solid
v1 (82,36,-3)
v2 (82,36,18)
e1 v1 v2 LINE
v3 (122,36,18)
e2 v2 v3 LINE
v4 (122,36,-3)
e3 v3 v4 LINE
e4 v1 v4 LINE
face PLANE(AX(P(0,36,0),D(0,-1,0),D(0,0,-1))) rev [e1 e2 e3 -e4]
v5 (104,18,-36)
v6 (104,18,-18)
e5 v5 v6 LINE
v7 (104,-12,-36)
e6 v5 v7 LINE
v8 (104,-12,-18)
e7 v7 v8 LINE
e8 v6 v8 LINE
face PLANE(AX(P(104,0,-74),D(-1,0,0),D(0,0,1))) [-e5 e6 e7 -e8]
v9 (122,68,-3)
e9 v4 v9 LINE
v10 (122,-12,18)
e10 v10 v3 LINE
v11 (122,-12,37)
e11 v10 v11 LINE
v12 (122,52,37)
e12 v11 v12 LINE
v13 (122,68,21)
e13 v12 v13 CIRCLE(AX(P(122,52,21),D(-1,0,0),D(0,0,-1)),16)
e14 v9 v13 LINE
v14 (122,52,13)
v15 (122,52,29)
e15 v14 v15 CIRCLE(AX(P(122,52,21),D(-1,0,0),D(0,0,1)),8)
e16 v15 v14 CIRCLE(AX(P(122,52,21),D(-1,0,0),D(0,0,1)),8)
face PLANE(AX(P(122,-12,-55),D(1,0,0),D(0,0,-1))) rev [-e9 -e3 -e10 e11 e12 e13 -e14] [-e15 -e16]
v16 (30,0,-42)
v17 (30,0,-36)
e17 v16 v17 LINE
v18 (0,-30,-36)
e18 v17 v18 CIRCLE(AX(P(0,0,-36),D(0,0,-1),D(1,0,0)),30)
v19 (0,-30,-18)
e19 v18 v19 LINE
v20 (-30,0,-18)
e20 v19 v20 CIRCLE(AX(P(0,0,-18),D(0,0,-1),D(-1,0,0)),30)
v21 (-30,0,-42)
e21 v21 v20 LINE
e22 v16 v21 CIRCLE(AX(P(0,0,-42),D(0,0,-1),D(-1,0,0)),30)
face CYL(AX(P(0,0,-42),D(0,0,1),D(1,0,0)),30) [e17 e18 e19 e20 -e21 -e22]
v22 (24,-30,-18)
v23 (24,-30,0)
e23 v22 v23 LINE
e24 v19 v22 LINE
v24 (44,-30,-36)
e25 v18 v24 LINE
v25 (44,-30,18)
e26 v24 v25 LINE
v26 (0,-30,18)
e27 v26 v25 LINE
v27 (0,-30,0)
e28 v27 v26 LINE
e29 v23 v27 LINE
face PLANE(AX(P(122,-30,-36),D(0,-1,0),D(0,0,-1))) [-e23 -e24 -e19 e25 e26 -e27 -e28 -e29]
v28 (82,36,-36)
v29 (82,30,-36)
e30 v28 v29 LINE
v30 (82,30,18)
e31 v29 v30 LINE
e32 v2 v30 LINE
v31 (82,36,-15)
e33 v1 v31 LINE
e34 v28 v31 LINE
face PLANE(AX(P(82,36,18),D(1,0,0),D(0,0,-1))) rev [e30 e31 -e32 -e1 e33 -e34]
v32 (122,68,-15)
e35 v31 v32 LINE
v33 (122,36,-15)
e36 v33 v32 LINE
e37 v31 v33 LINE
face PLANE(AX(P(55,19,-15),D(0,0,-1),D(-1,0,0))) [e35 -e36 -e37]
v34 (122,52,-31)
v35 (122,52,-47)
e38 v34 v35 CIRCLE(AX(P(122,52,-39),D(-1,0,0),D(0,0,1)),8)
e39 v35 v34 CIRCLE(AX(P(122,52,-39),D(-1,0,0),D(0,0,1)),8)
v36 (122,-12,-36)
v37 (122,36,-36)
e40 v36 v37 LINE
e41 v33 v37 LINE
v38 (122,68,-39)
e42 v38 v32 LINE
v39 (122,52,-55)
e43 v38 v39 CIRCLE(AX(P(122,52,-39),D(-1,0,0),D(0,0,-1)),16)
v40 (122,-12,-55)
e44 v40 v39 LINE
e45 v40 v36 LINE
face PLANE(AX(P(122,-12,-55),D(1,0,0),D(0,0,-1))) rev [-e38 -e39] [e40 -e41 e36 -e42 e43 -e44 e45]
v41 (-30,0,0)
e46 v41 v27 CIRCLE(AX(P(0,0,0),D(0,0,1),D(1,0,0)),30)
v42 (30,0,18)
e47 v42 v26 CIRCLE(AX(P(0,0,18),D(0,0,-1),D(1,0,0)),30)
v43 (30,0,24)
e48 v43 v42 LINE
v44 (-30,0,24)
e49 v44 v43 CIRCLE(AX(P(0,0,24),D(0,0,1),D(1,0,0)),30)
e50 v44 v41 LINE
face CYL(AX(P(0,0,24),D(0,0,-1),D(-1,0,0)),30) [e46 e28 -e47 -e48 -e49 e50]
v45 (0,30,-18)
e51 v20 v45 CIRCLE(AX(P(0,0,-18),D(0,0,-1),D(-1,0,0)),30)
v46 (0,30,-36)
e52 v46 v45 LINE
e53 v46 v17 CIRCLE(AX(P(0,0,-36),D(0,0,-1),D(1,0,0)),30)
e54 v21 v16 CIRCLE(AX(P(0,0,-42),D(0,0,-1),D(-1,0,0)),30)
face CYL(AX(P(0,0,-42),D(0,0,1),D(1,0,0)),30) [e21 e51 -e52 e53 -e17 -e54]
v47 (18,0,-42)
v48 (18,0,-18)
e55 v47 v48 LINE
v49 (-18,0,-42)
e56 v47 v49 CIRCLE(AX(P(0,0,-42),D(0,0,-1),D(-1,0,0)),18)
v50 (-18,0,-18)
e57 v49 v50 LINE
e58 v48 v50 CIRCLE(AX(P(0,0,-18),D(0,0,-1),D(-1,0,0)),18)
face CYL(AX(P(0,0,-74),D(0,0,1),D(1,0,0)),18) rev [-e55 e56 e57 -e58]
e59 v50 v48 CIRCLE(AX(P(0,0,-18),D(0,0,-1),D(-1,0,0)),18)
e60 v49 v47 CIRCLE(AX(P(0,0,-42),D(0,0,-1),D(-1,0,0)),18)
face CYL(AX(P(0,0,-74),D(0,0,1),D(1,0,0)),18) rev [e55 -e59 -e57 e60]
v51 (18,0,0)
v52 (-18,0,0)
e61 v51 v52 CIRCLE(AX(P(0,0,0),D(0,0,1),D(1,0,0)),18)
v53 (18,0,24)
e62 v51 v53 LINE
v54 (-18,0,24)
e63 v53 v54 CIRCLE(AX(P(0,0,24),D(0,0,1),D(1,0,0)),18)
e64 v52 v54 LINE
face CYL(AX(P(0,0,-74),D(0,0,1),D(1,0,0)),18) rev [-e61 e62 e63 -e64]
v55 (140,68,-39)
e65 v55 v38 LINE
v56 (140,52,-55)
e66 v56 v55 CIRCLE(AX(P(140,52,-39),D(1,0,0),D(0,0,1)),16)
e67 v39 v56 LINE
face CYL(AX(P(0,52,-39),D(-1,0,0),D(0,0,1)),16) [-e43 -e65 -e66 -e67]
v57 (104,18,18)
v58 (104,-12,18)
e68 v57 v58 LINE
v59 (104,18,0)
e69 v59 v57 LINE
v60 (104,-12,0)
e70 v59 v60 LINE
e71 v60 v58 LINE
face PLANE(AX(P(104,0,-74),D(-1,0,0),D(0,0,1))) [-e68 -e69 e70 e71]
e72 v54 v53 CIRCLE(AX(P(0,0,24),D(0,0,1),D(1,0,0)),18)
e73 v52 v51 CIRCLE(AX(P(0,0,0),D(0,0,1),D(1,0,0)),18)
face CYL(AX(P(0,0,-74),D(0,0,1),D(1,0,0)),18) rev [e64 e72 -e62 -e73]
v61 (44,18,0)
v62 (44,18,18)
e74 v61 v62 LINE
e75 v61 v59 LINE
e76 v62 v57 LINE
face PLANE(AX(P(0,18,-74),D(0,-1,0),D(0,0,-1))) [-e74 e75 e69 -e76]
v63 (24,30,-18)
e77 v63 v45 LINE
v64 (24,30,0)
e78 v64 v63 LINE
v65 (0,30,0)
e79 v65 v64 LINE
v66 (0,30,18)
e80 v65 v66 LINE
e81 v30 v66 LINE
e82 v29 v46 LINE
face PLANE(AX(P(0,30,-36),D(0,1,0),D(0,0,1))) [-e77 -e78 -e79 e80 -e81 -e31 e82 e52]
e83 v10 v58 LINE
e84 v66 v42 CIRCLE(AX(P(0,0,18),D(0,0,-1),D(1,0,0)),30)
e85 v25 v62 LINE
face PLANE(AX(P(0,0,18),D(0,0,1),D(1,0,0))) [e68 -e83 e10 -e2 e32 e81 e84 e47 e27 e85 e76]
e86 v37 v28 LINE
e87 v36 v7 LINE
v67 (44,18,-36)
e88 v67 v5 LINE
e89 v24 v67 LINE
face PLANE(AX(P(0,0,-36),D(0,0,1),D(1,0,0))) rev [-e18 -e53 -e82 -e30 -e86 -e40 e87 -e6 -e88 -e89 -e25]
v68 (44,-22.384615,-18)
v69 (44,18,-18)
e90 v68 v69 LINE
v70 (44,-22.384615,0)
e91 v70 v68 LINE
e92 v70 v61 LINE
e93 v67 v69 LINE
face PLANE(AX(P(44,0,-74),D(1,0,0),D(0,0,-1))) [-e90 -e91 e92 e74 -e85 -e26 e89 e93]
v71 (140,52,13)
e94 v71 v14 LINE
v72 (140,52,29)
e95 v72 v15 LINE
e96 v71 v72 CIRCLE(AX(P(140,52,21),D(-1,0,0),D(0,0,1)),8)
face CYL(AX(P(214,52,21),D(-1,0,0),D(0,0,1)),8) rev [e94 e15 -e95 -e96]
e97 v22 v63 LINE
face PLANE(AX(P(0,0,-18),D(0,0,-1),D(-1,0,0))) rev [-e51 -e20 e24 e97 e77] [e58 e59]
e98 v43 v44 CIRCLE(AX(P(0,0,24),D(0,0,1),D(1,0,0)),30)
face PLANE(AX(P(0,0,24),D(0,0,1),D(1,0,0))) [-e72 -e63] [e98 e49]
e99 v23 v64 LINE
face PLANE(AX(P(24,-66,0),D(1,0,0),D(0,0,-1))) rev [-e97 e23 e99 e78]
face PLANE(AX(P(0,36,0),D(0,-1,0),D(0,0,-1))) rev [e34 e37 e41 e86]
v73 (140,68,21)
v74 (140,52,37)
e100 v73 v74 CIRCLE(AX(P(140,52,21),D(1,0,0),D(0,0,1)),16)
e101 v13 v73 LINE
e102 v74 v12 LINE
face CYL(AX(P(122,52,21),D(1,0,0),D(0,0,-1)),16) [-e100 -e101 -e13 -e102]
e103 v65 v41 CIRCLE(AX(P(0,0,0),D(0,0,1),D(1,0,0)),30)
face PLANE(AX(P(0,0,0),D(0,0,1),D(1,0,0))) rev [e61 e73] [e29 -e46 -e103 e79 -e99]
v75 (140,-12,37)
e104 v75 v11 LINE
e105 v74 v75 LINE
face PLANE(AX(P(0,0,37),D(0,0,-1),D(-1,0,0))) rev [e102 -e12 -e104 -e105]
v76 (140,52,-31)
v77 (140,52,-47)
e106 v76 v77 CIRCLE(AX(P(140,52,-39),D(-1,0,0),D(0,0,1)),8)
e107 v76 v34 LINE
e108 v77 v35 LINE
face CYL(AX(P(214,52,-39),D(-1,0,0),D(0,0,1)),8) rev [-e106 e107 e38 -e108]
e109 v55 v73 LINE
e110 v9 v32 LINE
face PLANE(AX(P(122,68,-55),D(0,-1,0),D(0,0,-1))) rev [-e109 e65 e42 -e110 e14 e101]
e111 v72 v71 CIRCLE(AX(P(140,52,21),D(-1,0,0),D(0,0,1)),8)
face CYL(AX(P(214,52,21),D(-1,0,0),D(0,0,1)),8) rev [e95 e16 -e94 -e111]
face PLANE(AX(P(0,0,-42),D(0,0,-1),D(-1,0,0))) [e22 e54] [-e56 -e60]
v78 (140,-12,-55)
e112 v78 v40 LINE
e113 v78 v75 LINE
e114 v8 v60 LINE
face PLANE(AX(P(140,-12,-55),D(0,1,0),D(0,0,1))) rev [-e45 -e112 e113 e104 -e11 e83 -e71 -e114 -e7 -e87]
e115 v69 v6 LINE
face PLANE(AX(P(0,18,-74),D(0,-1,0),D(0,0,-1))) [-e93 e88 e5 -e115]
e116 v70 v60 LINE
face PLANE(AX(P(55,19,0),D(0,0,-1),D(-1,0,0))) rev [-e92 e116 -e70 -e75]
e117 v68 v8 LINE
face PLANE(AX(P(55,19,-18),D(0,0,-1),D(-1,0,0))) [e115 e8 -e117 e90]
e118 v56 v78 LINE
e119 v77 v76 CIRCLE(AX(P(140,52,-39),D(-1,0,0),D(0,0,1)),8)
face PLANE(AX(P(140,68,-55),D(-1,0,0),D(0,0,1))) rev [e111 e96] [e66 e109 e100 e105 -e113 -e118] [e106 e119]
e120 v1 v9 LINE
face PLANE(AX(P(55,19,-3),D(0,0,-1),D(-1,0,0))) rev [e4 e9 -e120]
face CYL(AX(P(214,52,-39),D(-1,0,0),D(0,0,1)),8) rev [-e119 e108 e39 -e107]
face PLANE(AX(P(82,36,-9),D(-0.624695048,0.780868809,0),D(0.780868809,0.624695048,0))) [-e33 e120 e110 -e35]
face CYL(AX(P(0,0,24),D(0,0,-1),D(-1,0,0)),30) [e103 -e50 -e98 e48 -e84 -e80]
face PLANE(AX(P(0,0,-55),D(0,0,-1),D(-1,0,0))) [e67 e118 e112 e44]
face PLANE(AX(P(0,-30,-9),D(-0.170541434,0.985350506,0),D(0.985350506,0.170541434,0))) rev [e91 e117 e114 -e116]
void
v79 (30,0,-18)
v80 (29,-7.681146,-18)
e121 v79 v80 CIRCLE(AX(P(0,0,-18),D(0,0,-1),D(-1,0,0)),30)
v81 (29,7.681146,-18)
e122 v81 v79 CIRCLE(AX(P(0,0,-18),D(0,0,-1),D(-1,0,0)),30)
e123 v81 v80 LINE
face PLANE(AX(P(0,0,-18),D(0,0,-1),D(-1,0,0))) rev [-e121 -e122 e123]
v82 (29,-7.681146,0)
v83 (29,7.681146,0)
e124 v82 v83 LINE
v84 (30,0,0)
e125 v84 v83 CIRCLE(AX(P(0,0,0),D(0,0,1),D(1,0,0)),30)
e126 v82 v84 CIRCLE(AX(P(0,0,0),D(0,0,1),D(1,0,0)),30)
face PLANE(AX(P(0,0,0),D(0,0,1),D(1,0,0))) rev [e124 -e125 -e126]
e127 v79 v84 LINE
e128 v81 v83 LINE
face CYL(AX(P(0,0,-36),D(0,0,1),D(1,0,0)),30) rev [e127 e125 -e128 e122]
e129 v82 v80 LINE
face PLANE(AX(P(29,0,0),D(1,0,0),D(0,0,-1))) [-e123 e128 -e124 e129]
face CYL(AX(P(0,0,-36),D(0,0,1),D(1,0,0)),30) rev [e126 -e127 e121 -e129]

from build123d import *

# Parameters (mm, degrees)
HUB_PROFILE_SKETCH_R         = 30
HUB_60_DEPTH                 = 24
HUB_EXTENSION_SKETCH_R       = 30
HUB_EXTENSION_60_DEPTH       = 24
HUB_BORE_SKETCH_R            = 18
HUB_BORE_36_DEPTH            = 98
ARM_START                    = -54
ARM_BODY_DEPTH               = 54
CLEVIS_SLOT_SKETCH_W         = 24
CLEVIS_SLOT_SKETCH_H         = 18
CLEVIS_SLOT_24MM_DEPTH       = 96
SLOT_PAD_SKETCH_W            = 18
SLOT_PAD_SKETCH_H            = 60
SLOT_PAD_5MM_DEPTH           = 5
RIB_BASE_PAD_SKETCH_W        = 40
RIB_BASE_PAD_SKETCH_H        = 54
RIB_BASE_PAD_DEPTH           = 6
MOUNTING_FLANGE_SKETCH_W     = 18
MOUNTING_FLANGE_SKETCH_H     = 80
MOUNTING_FLANGE_DEPTH        = 46
FLANGE_CORNER_FILLET_R16_A_R = 16
FLANGE_CORNER_FILLET_R16_B_R = 16
FLANGE_HOLES_SKETCH_R        = 8
FLANGE_HOLES_2X_16_DEPTH     = 92
FLANGE_RIB_12MM_REACH        = 164.296
FLANGE_RIB_SKETCH_WALL_W     = 377.817045558
FLANGE_RIB_SKETCH_WALL_H     = 12
ARM_RELIEF_CUT_DEPTH         = 92
ARM_RIB_18MM_REACH           = 164.296
ARM_RIB_SKETCH_WALL_W        = 432.138250074
ARM_RIB_SKETCH_WALL_H        = 18


with BuildPart() as part:
    # Hub Profile Sketch → Hub Ø60 (new body)
    with BuildSketch(Plane.XY):
        Circle(HUB_PROFILE_SKETCH_R)
    extrude(amount=HUB_60_DEPTH)


with BuildPart() as body_2:
    # Hub Extension Sketch → Hub Extension Ø60 (new body)
    with BuildSketch(Plane(origin=(0, 0, -18), x_dir=(-1, 0, 0), z_dir=(0, 0, -1))):
        with Locations(Location((0, 0, 0), (0, 0, 180))):
            Circle(HUB_EXTENSION_SKETCH_R)
    extrude(amount=HUB_EXTENSION_60_DEPTH)


with BuildPart() as hub_bore_36_tool:
    # Hub Bore Sketch → Hub Bore Ø36 (new body)
    with BuildSketch(Plane.XY.offset(24)):
        Circle(HUB_BORE_SKETCH_R)
    extrude(amount=-HUB_BORE_36_DEPTH)


with BuildPart() as part_1:
    add(part.part)

    # Hub Bore Ø36: cut by hub_bore_36_tool
    add(hub_bore_36_tool.part, mode=Mode.SUBTRACT)



with BuildPart() as body_2_1:
    add(body_2.part)

    # Hub Bore Ø36: cut by hub_bore_36_tool
    add(hub_bore_36_tool.part, mode=Mode.SUBTRACT)


with BuildPart() as part_2:
    add(part_1.part)

    add(body_2_1.part)  # Arm Body merges body 2
    # Arm Profile Sketch → Arm Body (add)
    with BuildSketch(Plane.XY.offset(18).offset(ARM_START)):
        with BuildLine():
            Line((0, 30), (122, 30))
            Line((122, 30), (122, -30))
            Line((122, -30), (0, -30))
            ThreePointArc((0, -30), (30, 0), (0, 30))
        make_face()
    extrude(amount=ARM_BODY_DEPTH)

    # Clevis Slot Sketch → Clevis Slot 24mm (cut)
    with BuildSketch(Plane(origin=(0, 30, 0), x_dir=(1, 0, 0), z_dir=(0, 1, 0))):
        with Locations((12, 9)):
            Rectangle(CLEVIS_SLOT_SKETCH_W, CLEVIS_SLOT_SKETCH_H)
    extrude(amount=-CLEVIS_SLOT_24MM_DEPTH, mode=Mode.SUBTRACT)

    # Slot Pad Sketch → Slot Pad 5mm (add)
    with BuildSketch(Plane.ZY.offset(-24)):
        with Locations((-9, 0)):
            Rectangle(SLOT_PAD_SKETCH_W, SLOT_PAD_SKETCH_H)
    extrude(amount=-SLOT_PAD_5MM_DEPTH)

    # Rib Base Pad Sketch → Rib Base Pad (add)
    with BuildSketch(Plane(origin=(0, 30, 0), x_dir=(1, 0, 0), z_dir=(0, 1, 0))):
        with Locations((102, 9)):
            Rectangle(RIB_BASE_PAD_SKETCH_W, RIB_BASE_PAD_SKETCH_H)
    extrude(amount=RIB_BASE_PAD_DEPTH)

    # Mounting Flange Sketch → Mounting Flange (add, symmetric)
    with BuildSketch(Plane(origin=(0, 0, -9), x_dir=(-1, 0, 0), z_dir=(0, 0, -1))):
        with Locations((-131, 28)):
            Rectangle(MOUNTING_FLANGE_SKETCH_W, MOUNTING_FLANGE_SKETCH_H)
    extrude(amount=MOUNTING_FLANGE_DEPTH, both=True)

    # Flange Corner Fillet R16 A
    flange_corner_fillet_r16_a_edges = [part_2.edges().sort_by_distance(p)[0] for p in [
        (131, 68, 37),
    ]]
    fillet(flange_corner_fillet_r16_a_edges, radius=FLANGE_CORNER_FILLET_R16_A_R)

    # Flange Corner Fillet R16 B
    flange_corner_fillet_r16_b_edges = [part_2.edges().sort_by_distance(p)[0] for p in [
        (131, 68, -55),
    ]]
    fillet(flange_corner_fillet_r16_b_edges, radius=FLANGE_CORNER_FILLET_R16_B_R)

    # Flange Holes Sketch → Flange Holes 2xØ16 (cut)
    with BuildSketch(Plane.ZY.offset(-122)):
        with Locations((21, 52)):
            Circle(FLANGE_HOLES_SKETCH_R)
        with Locations((-39, 52)):
            Circle(FLANGE_HOLES_SKETCH_R)
    extrude(amount=-FLANGE_HOLES_2X_16_DEPTH, mode=Mode.SUBTRACT)

    # Flange Rib Sketch wall → Flange Rib 12mm (add, up to next)
    with BuildSketch(Plane(origin=(102, 52, -9), x_dir=(0.780868809443, 0.624695047554, 0), z_dir=(0.624695047554, -0.780868809443, 0)), mode=Mode.PRIVATE) as flange_rib_12mm_sk1:
        Rectangle(FLANGE_RIB_SKETCH_WALL_W, FLANGE_RIB_SKETCH_WALL_H)
    flange_rib_12mm_tool1 = extrude(flange_rib_12mm_sk1.sketch, amount=FLANGE_RIB_12MM_REACH, mode=Mode.PRIVATE) - part_2.part
    add(flange_rib_12mm_tool1.solids().sort_by_distance((102, 52, -9))[0])

    # Arm Relief Sketch → Arm Relief Cut (cut)
    with BuildSketch(Plane.XY.offset(18)):
        Polygon((104, 18), (104, -12), (44, -30), (44, 18), align=None)
        Polygon((122, -30), (122, -12), (104, -12), (44, -30), align=None)
    extrude(amount=-ARM_RELIEF_CUT_DEPTH, mode=Mode.SUBTRACT)

    # Arm Rib Sketch wall → Arm Rib 18mm (add, up to next)
    with BuildSketch(Plane(origin=(52, -21, -9), x_dir=(0.985350505855, 0.170541433706, 0), z_dir=(0.170541433706, -0.985350505855, 0)), mode=Mode.PRIVATE) as arm_rib_18mm_sk1:
        Rectangle(ARM_RIB_SKETCH_WALL_W, ARM_RIB_SKETCH_WALL_H)
    arm_rib_18mm_tool1 = extrude(arm_rib_18mm_sk1.sketch, amount=-ARM_RIB_18MM_REACH, mode=Mode.PRIVATE) - part_2.part
    add(arm_rib_18mm_tool1.solids().sort_by_distance((52, -21, -9))[0])


solid = part_2.part
